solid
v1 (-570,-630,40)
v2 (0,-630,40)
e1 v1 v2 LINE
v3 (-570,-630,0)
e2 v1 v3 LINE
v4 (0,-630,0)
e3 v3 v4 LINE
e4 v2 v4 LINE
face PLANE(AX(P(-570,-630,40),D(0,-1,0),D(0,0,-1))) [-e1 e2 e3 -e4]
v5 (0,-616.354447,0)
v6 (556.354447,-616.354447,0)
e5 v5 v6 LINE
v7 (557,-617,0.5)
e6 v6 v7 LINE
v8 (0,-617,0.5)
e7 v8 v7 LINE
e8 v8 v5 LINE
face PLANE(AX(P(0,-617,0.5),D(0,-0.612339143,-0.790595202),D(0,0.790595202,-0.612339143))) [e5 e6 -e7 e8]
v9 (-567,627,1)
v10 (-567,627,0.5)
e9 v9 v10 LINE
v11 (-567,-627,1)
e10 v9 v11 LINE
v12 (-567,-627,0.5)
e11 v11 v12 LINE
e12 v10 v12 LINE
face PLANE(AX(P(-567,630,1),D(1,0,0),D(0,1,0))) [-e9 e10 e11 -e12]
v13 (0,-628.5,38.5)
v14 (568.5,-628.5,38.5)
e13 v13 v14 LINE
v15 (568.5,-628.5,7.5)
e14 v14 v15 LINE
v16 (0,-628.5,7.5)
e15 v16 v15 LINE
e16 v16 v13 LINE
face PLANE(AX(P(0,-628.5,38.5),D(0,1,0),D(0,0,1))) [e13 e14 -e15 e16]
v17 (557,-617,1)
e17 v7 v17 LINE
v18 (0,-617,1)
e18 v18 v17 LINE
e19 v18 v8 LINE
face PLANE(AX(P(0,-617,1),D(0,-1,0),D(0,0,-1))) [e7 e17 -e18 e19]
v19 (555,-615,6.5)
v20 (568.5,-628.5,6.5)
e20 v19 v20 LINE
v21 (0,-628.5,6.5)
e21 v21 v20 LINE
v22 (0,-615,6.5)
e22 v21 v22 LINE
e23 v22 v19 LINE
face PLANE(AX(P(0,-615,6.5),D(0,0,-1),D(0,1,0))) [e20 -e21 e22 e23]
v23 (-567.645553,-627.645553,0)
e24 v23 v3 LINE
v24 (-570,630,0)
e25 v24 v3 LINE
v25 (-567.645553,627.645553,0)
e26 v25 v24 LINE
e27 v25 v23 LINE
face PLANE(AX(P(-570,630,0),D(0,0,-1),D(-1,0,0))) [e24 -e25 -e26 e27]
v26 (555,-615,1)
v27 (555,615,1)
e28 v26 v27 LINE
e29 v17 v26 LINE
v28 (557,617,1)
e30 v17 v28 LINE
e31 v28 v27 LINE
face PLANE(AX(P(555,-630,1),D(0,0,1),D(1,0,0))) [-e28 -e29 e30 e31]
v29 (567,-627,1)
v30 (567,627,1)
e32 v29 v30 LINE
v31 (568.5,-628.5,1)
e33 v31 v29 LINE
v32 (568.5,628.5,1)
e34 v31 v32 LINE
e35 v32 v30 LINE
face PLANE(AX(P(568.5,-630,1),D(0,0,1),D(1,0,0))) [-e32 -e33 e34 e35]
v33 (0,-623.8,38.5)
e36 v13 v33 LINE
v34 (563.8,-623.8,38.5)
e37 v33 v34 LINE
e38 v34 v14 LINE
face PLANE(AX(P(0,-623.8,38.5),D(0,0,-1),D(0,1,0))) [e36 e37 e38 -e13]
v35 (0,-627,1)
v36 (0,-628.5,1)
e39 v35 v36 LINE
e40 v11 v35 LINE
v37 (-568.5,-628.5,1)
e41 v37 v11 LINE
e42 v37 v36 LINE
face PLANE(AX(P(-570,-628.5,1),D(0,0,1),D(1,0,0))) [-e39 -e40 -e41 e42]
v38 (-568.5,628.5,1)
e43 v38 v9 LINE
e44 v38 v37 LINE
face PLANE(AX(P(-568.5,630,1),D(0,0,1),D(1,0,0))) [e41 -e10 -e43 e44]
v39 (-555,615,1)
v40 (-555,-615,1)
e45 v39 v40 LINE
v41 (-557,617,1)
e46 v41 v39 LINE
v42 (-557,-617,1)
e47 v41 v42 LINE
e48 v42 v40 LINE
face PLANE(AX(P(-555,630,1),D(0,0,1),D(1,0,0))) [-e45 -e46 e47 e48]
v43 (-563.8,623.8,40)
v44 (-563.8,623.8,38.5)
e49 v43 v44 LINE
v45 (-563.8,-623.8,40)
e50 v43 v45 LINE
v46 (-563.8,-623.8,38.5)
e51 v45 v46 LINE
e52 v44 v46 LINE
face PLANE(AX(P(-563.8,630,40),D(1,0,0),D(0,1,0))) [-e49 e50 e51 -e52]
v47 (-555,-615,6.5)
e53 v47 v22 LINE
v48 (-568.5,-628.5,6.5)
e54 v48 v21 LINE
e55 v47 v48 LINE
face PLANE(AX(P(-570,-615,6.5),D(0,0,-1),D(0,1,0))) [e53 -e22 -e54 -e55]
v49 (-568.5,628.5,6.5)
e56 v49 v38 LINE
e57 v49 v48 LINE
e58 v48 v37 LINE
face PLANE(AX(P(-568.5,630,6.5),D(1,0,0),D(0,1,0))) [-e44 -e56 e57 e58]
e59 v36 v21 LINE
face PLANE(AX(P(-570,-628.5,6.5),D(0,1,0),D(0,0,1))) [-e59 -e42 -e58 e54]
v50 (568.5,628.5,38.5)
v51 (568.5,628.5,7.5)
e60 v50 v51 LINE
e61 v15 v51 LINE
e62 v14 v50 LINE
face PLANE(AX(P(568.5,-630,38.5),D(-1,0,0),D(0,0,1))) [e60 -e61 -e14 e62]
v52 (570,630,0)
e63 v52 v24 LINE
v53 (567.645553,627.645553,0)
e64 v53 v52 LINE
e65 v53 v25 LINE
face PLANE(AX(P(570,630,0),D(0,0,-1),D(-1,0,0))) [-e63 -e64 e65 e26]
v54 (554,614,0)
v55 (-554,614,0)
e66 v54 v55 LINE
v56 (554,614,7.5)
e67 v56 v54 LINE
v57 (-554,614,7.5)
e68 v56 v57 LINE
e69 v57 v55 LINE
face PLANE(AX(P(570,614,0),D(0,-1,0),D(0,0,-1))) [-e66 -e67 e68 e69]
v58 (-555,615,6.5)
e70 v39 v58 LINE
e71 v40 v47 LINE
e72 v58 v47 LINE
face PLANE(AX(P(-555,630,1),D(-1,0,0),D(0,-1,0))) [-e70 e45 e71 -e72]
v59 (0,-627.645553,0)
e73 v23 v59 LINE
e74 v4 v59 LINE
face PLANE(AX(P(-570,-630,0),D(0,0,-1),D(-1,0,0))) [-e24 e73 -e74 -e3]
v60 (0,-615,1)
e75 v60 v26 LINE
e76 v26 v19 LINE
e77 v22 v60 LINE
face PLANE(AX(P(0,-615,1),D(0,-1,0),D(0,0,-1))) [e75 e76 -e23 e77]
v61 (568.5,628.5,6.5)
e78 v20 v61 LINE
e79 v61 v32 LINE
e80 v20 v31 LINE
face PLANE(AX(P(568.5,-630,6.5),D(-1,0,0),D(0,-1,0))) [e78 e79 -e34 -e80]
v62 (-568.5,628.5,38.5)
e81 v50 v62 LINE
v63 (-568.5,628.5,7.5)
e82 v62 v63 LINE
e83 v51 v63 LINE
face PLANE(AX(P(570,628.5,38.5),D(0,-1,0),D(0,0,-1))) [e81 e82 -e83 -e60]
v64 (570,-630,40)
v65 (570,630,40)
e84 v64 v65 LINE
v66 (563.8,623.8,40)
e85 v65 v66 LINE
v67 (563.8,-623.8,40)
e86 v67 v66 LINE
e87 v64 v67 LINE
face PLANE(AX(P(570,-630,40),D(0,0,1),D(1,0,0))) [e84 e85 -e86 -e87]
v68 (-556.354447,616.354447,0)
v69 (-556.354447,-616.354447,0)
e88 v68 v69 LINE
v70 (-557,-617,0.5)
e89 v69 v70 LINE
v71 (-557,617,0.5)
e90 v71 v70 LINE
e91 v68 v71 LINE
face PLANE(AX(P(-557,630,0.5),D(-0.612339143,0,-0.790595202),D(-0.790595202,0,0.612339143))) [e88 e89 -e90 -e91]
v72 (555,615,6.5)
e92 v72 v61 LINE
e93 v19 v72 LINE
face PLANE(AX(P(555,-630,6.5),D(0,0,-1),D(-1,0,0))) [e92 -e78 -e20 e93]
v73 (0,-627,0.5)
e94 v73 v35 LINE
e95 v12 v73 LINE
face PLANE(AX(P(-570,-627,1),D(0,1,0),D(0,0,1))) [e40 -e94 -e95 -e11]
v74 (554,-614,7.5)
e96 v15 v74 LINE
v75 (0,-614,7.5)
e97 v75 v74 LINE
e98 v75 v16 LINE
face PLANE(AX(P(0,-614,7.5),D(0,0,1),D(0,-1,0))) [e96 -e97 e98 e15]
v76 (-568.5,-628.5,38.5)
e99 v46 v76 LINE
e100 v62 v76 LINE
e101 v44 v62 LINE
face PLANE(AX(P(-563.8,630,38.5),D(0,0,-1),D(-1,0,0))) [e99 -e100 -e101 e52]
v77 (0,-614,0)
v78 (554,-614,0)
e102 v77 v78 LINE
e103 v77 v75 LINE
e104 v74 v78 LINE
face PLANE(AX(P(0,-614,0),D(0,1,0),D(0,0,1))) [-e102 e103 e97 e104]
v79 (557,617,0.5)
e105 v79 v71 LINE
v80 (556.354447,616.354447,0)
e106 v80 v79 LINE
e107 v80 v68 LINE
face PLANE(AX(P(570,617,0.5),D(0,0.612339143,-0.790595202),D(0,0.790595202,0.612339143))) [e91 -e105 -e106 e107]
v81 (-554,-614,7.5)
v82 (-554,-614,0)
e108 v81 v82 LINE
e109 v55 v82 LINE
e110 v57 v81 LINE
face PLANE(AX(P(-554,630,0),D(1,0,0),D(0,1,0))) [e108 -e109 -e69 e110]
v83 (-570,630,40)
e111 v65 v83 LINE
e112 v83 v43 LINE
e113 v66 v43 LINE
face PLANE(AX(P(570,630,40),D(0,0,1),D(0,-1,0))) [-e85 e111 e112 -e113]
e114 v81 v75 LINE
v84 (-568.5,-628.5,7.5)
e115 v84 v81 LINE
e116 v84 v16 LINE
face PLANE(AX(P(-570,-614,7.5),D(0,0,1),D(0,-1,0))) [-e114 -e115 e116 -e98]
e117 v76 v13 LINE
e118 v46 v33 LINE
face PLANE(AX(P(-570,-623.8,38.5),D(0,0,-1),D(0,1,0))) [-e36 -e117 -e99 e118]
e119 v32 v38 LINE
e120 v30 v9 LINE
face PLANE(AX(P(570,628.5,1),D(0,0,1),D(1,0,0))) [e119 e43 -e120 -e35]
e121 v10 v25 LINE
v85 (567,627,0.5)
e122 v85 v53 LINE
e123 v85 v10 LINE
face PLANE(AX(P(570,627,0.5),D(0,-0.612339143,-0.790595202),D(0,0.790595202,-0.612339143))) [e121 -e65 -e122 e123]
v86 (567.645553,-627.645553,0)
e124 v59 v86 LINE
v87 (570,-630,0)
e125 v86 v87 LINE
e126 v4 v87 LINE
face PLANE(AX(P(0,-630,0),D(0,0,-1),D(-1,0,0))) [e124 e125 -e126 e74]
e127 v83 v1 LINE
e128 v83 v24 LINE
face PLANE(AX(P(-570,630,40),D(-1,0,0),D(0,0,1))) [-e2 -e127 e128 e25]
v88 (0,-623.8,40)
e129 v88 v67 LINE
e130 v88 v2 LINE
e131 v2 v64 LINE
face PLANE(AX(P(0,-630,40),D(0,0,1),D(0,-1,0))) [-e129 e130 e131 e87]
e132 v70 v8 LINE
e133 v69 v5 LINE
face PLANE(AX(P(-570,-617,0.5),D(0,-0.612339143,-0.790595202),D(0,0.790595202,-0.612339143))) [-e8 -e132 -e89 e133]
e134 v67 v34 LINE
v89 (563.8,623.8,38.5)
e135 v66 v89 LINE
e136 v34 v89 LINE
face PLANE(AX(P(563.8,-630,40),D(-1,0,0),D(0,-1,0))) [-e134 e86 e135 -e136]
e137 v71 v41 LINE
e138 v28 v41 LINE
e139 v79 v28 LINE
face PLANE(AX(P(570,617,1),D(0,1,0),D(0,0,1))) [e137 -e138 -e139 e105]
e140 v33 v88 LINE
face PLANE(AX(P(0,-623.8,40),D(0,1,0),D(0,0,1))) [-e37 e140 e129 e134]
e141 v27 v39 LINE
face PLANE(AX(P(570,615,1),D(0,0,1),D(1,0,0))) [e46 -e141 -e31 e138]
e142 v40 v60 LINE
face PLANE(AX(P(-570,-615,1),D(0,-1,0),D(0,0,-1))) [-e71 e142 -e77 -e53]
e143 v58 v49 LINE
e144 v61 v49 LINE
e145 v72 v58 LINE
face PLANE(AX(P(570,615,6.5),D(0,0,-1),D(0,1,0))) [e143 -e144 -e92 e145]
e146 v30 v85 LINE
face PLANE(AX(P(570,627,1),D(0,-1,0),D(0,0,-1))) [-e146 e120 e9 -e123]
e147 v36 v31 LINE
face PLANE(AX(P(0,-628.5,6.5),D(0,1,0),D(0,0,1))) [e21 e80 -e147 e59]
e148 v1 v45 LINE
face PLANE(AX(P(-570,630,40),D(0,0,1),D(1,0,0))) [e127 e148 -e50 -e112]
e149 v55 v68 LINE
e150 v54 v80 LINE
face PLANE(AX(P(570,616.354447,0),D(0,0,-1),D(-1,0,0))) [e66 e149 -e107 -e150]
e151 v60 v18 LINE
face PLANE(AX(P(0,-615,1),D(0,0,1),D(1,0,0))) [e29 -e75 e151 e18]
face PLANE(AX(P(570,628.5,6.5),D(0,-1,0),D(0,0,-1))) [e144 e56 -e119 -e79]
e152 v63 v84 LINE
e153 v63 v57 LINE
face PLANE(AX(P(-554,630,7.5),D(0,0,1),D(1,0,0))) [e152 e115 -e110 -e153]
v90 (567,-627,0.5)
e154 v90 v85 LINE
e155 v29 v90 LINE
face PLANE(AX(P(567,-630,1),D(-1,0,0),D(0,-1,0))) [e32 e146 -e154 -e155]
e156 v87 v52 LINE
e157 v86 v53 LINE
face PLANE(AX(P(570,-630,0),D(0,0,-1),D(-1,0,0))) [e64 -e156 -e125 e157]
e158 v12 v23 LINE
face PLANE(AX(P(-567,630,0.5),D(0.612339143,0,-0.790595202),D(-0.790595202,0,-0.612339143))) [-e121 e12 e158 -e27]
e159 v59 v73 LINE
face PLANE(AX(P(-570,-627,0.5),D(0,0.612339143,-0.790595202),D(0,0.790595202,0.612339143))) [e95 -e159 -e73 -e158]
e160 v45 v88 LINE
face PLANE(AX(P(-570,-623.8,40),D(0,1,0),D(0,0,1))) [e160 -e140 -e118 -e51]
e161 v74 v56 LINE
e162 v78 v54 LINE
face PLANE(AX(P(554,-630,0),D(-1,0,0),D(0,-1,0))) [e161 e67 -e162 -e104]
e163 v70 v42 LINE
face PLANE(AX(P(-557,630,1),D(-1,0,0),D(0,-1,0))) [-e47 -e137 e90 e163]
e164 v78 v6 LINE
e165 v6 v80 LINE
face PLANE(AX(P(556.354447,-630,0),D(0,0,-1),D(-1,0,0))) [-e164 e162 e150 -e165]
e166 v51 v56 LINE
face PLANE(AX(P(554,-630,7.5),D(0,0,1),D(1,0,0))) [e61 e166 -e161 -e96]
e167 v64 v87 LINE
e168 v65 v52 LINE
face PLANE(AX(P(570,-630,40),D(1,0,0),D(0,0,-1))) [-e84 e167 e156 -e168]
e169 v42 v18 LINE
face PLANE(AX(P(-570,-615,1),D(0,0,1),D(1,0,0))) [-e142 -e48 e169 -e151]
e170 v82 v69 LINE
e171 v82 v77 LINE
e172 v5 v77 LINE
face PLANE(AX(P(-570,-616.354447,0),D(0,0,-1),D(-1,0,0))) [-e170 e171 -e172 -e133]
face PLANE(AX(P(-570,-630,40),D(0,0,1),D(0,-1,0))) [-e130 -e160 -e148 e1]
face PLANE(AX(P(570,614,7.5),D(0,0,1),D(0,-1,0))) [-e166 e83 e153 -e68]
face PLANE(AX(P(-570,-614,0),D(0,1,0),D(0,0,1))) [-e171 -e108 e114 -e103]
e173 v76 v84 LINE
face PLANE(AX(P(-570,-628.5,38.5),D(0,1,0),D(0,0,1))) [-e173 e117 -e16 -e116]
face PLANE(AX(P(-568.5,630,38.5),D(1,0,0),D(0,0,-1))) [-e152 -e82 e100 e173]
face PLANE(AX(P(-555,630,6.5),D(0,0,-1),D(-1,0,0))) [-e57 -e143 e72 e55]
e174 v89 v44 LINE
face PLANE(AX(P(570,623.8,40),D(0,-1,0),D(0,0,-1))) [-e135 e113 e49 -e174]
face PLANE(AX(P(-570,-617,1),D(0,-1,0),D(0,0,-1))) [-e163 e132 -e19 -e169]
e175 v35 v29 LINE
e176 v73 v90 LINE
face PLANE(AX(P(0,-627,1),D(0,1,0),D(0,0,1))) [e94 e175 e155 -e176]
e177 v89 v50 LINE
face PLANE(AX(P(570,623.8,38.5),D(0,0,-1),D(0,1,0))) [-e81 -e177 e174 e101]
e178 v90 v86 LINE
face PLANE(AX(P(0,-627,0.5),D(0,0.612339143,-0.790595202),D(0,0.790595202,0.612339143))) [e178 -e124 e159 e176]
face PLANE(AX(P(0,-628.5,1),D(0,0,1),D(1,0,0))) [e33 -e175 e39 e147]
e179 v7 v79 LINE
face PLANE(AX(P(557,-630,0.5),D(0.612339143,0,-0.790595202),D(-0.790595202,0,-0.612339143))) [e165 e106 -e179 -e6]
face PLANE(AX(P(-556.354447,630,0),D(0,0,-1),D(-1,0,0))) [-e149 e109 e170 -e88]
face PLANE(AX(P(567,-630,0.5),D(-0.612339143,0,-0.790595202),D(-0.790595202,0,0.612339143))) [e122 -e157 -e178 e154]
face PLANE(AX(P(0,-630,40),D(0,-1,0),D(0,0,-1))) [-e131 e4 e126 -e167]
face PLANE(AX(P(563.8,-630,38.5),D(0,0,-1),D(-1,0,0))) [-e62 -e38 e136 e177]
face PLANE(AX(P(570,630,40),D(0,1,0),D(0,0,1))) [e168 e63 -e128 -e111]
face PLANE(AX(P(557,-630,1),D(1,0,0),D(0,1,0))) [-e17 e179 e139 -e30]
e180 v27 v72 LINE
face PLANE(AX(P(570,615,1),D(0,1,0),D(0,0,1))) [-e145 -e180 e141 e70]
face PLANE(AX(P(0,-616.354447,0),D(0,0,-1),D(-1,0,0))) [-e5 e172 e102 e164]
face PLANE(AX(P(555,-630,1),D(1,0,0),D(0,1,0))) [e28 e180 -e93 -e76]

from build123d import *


with BuildPart() as part:
    # 扫描4: sweep along a path in 草图1
    with BuildLine(Plane.XY) as sweep_4_path:
        Line((-570, 630), (570, 630))
        Line((570, 630), (570, -630))
        Line((570, -630), (-570, -630))
        Line((-570, -630), (-570, 630))
    # 草图5 → 扫描4 (sweep)
    with BuildSketch(Plane(origin=(0, 0, 0), x_dir=(0, 0, -1), z_dir=(1, 0, 0))):
        Polygon((-40, -630), (0, -630), (0, -627.645553376), (-0.5, -627), (-1, -627), (-1, -628.5), (-6.5, -628.5), (-6.5, -615), (-1, -615), (-1, -617), (-0.5, -617), (0, -616.354446624), (0, -614), (-7.5, -614), (-7.5, -628.5), (-38.5, -628.5), (-38.5, -623.8), (-40, -623.8), align=None)
    sweep(path=sweep_4_path.line, transition=Transition.RIGHT)


solid = part.part
